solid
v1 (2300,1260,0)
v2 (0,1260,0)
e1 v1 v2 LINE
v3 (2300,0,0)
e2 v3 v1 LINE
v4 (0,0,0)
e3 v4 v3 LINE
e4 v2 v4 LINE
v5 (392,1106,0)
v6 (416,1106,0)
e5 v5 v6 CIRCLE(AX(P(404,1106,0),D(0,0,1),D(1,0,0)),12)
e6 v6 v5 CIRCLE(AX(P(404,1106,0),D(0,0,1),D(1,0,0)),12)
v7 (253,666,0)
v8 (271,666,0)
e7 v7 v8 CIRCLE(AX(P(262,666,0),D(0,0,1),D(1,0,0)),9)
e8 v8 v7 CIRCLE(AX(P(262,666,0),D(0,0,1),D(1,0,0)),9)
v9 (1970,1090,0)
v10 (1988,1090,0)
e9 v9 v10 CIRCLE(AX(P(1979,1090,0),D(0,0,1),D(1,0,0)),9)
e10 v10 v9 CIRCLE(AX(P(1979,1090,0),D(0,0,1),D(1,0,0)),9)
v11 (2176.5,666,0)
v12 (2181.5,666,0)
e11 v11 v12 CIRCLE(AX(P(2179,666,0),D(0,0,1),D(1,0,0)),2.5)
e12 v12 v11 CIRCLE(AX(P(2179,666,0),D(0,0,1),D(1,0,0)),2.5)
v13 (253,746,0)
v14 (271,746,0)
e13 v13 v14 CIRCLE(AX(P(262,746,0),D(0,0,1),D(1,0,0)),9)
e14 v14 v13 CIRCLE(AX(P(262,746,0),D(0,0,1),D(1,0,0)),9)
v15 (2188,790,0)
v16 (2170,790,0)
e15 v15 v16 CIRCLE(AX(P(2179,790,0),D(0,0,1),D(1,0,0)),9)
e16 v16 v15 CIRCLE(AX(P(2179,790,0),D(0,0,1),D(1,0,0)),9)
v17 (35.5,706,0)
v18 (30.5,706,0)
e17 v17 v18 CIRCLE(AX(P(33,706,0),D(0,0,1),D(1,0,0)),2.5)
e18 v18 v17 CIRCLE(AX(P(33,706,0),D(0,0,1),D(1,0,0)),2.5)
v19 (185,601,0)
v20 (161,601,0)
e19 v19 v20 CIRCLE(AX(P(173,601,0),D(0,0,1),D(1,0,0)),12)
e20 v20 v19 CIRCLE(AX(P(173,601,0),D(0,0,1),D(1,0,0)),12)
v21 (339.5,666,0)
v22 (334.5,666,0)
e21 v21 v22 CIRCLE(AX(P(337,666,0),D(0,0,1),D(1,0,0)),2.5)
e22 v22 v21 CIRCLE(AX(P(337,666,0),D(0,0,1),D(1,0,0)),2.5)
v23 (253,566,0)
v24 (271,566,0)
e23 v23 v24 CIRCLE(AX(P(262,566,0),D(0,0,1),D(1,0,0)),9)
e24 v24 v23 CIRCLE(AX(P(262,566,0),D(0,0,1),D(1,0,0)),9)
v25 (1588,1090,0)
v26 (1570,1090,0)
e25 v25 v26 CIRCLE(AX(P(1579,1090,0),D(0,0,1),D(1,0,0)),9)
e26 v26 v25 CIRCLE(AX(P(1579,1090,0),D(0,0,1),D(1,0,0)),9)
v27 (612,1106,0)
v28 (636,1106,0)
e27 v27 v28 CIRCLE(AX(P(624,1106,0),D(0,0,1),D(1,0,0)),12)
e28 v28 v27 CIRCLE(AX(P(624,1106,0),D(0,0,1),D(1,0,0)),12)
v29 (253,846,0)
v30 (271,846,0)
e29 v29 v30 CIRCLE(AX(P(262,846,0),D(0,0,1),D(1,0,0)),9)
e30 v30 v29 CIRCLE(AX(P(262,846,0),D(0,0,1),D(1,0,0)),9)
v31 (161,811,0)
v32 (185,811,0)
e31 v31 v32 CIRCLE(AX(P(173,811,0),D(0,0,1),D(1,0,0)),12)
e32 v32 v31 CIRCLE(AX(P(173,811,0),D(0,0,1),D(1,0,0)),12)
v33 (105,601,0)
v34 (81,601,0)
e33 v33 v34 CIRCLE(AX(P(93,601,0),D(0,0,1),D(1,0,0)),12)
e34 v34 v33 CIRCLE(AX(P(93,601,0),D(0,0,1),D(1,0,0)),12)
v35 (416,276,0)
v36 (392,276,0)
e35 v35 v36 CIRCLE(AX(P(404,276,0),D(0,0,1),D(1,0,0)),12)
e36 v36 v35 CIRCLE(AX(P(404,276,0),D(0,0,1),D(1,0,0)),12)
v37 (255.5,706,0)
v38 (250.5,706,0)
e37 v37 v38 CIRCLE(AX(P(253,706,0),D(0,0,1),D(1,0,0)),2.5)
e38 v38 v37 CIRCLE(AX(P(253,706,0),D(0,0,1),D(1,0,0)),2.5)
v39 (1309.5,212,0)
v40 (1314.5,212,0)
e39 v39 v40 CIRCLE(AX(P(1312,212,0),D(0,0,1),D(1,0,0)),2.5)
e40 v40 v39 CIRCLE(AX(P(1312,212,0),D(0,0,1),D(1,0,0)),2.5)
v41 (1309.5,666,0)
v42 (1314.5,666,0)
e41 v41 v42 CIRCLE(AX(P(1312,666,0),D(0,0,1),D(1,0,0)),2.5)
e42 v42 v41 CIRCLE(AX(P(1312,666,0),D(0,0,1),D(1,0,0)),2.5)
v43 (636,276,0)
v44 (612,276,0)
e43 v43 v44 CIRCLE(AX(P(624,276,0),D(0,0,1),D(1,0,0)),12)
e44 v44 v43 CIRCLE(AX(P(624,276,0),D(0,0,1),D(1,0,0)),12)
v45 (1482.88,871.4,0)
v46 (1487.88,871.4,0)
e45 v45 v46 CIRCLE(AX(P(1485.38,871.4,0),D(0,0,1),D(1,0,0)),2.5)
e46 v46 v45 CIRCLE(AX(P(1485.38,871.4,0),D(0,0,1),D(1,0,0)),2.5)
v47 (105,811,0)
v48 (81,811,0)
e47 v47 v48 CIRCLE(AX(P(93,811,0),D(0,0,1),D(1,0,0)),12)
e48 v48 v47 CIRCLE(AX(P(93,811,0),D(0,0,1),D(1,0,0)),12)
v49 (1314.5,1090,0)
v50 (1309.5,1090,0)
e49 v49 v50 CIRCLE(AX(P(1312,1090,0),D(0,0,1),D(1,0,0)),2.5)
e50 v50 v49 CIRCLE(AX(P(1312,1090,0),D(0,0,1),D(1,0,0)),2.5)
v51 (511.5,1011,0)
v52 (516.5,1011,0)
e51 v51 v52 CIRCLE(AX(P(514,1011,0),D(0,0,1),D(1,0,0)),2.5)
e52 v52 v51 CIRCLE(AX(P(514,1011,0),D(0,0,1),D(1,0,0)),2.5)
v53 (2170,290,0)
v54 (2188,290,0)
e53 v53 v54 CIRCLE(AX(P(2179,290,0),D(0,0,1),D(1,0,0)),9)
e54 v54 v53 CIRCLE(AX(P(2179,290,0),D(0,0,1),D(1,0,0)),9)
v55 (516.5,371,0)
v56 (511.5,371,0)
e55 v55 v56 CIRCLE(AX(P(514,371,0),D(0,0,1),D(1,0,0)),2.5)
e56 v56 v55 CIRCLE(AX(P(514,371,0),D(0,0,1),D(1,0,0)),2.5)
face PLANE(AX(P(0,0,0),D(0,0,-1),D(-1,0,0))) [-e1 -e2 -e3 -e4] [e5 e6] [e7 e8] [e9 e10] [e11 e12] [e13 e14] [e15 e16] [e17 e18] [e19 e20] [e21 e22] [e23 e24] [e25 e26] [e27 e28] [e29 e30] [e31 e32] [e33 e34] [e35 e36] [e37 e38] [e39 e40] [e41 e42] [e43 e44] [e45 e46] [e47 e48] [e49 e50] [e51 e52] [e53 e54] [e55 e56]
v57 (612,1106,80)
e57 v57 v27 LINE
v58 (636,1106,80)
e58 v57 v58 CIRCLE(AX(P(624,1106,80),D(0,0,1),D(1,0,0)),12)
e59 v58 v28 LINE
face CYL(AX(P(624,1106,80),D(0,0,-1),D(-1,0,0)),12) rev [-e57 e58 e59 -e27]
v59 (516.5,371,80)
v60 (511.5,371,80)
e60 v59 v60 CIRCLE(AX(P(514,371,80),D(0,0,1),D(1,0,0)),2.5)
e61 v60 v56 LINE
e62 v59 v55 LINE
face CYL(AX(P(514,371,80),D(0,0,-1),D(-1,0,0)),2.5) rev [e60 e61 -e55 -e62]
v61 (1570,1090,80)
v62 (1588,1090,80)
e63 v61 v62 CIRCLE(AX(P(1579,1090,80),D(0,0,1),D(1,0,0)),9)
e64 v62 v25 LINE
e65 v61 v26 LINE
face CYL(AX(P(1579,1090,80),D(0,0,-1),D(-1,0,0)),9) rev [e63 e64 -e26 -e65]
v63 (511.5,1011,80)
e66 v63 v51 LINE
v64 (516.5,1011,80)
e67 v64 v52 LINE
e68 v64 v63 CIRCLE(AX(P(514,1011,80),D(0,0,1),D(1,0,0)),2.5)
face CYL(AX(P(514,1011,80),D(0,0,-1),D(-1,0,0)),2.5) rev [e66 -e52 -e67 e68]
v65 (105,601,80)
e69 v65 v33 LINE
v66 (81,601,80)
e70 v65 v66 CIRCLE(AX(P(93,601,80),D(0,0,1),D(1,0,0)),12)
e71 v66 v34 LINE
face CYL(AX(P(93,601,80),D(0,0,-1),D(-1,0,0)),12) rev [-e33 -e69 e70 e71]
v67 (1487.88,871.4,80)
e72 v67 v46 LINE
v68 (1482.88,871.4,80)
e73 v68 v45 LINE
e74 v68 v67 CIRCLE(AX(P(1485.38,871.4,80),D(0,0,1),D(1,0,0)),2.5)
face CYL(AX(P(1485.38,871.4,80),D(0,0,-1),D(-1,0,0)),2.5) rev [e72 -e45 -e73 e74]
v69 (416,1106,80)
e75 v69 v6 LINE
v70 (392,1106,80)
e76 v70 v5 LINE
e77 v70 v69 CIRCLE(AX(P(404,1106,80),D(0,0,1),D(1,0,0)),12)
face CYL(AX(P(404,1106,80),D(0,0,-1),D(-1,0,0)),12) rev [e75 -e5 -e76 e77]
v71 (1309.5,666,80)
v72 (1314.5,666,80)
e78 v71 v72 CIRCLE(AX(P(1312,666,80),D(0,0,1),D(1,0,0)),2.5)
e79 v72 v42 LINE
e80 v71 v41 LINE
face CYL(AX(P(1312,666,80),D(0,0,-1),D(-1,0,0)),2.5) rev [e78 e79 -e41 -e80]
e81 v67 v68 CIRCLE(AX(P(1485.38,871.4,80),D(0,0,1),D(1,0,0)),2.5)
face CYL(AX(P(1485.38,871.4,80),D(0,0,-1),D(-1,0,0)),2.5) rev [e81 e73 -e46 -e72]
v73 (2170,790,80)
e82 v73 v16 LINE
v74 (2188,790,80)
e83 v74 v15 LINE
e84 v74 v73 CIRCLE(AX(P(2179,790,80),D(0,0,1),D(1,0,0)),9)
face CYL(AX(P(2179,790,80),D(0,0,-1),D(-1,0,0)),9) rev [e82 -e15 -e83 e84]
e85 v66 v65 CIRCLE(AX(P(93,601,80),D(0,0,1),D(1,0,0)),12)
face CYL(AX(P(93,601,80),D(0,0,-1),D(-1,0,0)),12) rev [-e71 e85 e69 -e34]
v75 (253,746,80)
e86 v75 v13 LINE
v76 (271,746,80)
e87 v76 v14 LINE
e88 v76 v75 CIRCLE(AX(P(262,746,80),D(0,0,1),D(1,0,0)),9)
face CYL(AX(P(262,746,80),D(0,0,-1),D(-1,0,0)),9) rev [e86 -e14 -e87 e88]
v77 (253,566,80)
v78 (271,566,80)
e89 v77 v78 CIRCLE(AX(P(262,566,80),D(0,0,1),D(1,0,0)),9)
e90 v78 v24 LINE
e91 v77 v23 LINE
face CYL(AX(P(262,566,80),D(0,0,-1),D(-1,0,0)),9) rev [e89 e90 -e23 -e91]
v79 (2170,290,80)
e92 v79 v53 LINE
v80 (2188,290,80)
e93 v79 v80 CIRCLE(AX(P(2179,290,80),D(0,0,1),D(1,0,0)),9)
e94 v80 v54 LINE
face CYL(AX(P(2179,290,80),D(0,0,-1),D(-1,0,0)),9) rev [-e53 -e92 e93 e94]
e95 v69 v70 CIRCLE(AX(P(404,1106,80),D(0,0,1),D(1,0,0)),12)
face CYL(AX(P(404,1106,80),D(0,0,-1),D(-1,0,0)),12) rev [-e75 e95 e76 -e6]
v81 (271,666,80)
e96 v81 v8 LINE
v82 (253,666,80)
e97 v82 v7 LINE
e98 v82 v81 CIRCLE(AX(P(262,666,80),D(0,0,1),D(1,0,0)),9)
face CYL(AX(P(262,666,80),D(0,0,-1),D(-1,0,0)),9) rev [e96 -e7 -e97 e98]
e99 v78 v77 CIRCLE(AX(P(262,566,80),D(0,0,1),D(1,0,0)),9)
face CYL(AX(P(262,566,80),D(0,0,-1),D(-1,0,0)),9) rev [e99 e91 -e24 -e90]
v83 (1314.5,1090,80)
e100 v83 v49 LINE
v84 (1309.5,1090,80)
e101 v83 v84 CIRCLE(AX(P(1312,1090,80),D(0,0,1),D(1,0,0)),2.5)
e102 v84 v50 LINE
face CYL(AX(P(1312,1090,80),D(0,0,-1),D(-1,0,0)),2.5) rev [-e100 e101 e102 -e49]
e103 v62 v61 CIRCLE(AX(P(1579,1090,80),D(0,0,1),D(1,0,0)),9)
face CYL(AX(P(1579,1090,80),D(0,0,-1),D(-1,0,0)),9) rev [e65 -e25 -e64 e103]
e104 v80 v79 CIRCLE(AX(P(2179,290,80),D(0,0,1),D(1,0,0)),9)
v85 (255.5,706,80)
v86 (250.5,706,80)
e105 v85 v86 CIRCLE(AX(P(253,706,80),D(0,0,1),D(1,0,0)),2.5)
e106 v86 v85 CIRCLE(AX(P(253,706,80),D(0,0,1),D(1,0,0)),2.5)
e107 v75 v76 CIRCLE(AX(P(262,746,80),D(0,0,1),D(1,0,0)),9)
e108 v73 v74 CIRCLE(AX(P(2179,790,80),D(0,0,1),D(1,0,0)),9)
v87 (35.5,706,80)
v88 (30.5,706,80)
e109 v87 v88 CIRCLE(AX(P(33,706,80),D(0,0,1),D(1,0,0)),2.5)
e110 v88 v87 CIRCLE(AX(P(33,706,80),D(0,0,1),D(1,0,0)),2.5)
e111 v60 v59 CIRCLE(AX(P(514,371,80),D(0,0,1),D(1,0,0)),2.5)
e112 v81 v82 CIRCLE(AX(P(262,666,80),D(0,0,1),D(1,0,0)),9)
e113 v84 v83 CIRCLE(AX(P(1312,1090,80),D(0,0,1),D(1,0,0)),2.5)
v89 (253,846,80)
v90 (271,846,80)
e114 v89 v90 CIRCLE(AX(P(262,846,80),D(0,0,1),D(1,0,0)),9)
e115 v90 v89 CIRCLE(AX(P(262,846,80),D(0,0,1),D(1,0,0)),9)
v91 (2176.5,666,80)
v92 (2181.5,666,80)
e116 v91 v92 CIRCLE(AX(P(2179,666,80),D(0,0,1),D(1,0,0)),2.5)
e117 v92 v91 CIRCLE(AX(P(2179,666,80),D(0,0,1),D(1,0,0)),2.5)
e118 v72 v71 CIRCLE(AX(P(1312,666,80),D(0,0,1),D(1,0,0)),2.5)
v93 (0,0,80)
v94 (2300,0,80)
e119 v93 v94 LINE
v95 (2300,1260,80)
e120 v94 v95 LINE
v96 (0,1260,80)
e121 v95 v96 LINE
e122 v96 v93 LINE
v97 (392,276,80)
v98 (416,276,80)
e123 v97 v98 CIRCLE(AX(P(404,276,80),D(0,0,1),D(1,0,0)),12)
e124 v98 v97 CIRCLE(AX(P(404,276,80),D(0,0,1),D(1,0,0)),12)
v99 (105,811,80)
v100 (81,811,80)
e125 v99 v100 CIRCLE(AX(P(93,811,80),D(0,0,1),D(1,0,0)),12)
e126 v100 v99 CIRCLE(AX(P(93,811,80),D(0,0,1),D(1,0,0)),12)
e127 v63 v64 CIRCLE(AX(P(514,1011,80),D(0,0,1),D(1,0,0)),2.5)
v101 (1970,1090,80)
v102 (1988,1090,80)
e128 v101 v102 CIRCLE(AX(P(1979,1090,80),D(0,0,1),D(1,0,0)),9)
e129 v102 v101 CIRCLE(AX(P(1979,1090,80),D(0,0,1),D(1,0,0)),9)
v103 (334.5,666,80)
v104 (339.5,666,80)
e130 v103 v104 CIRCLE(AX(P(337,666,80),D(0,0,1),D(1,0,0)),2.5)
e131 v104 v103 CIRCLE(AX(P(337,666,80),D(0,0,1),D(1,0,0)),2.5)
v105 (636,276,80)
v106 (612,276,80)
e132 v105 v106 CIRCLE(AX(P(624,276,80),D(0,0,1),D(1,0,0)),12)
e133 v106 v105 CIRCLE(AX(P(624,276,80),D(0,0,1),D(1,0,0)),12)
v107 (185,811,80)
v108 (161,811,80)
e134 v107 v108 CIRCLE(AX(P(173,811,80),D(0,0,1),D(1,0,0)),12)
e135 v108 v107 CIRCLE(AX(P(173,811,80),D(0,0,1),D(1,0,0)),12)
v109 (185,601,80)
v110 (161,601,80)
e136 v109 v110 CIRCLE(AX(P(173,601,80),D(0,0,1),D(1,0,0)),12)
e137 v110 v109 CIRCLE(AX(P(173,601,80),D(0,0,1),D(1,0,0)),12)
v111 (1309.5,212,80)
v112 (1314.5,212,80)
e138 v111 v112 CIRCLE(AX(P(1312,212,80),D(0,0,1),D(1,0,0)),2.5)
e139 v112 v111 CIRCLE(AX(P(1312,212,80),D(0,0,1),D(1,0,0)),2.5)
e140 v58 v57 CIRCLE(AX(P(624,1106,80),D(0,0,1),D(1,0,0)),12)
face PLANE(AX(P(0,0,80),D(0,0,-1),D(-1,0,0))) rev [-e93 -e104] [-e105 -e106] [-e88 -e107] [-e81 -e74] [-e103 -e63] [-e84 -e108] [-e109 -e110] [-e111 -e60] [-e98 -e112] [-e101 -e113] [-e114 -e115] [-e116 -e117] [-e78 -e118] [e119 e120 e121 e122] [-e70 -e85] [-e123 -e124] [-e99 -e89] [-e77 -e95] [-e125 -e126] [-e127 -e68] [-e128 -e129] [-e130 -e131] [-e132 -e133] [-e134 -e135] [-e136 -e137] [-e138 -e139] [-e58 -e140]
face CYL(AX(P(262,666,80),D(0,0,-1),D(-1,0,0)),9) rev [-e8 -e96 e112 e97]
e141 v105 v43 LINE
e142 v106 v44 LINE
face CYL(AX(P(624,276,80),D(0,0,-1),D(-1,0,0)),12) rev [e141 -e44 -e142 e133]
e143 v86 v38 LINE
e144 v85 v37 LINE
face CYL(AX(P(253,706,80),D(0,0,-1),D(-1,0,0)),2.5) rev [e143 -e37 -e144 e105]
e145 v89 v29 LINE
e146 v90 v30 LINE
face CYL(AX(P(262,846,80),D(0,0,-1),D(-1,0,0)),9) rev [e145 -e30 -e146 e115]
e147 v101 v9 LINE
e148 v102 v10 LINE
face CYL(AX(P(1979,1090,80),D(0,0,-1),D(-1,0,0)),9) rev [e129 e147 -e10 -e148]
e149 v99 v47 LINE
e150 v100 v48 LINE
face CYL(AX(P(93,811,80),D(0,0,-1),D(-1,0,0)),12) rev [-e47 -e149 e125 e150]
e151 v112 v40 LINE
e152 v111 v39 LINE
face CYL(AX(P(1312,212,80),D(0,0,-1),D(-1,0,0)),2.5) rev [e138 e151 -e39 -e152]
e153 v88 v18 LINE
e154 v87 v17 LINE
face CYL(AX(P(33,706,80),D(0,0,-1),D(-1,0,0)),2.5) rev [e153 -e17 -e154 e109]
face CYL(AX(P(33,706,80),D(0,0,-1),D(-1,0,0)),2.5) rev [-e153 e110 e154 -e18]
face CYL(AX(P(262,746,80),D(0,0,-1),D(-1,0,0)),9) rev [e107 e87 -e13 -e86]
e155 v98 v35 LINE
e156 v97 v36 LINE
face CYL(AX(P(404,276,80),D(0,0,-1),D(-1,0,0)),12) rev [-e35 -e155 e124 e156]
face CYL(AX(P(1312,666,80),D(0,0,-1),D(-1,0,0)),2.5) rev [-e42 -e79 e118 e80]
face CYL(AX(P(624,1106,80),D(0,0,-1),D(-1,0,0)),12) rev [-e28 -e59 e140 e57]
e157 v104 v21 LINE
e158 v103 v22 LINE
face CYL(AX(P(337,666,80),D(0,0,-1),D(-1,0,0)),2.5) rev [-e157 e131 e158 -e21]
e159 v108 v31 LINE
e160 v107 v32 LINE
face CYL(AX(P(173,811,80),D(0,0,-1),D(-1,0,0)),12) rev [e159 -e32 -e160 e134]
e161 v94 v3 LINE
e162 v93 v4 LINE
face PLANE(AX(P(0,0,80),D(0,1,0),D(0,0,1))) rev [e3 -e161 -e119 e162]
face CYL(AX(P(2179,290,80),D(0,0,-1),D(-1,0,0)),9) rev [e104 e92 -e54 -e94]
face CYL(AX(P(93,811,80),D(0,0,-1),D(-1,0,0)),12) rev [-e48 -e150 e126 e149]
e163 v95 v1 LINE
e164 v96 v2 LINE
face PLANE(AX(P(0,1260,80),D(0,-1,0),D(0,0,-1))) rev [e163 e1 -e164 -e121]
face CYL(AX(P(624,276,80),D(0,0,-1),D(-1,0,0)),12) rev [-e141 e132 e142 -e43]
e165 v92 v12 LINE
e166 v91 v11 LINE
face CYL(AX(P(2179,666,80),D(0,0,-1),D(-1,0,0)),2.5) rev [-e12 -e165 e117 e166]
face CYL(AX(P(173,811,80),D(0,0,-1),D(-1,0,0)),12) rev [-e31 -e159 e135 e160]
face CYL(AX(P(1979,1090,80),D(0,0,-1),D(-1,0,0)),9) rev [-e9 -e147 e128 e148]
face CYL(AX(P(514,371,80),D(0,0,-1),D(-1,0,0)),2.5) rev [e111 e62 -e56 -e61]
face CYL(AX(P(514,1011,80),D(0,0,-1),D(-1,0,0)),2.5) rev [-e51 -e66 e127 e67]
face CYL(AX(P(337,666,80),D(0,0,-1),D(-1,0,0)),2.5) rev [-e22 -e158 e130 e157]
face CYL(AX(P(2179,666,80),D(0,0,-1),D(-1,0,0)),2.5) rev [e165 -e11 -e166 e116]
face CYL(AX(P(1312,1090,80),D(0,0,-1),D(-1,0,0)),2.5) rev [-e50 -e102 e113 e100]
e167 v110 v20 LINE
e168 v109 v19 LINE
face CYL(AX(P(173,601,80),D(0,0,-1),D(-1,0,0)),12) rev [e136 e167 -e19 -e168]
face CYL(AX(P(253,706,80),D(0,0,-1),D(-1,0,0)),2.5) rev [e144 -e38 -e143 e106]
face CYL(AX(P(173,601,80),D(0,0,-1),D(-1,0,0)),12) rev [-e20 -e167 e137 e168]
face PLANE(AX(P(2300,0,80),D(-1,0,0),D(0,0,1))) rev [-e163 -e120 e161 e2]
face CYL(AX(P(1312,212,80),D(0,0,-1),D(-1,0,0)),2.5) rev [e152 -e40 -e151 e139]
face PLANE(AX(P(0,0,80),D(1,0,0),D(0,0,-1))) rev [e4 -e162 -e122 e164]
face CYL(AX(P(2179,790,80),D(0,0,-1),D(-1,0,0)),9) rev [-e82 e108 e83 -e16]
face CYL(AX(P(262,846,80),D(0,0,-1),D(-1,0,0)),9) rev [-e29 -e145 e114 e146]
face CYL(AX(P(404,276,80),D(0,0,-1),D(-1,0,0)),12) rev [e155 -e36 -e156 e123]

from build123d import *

# Parameters (mm, degrees)
SKETCH1_W           = 2300
SKETCH1_H           = 1260
SKETCH1_R           = 9
SKETCH1_R_2         = 12
SKETCH1_R_3         = 2.5
BOSS_EXTRUDE1_DEPTH = 80


with BuildPart() as part:
    # Sketch1 → Boss-Extrude1 (new body)
    with BuildSketch(Plane.XY):
        with Locations((1150, 630)):
            Rectangle(SKETCH1_W, SKETCH1_H)
        with Locations((1579, 1090)):
            Circle(SKETCH1_R, mode=Mode.SUBTRACT)
        with Locations((1979, 1090)):
            Circle(SKETCH1_R, mode=Mode.SUBTRACT)
        with Locations((2179, 790)):
            Circle(SKETCH1_R, mode=Mode.SUBTRACT)
        with Locations((2179, 290)):
            Circle(SKETCH1_R, mode=Mode.SUBTRACT)
        with Locations((93, 811)):
            Circle(SKETCH1_R_2, mode=Mode.SUBTRACT)
        with Locations((173, 811)):
            Circle(SKETCH1_R_2, mode=Mode.SUBTRACT)
        with Locations((93, 601)):
            Circle(SKETCH1_R_2, mode=Mode.SUBTRACT)
        with Locations((173, 601)):
            Circle(SKETCH1_R_2, mode=Mode.SUBTRACT)
        with Locations((404, 1106)):
            Circle(SKETCH1_R_2, mode=Mode.SUBTRACT)
        with Locations((624, 1106)):
            Circle(SKETCH1_R_2, mode=Mode.SUBTRACT)
        with Locations((404, 276)):
            Circle(SKETCH1_R_2, mode=Mode.SUBTRACT)
        with Locations((624, 276)):
            Circle(SKETCH1_R_2, mode=Mode.SUBTRACT)
        with Locations((2179, 666)):
            Circle(SKETCH1_R_3, mode=Mode.SUBTRACT)
        with Locations((337, 666)):
            Circle(SKETCH1_R_3, mode=Mode.SUBTRACT)
        with Locations((1312, 666)):
            Circle(SKETCH1_R_3, mode=Mode.SUBTRACT)
        with Locations((1485.38, 871.4)):
            Circle(SKETCH1_R_3, mode=Mode.SUBTRACT)
        with Locations((1312, 1090)):
            Circle(SKETCH1_R_3, mode=Mode.SUBTRACT)
        with Locations((1312, 212)):
            Circle(SKETCH1_R_3, mode=Mode.SUBTRACT)
        with Locations((514, 371)):
            Circle(SKETCH1_R_3, mode=Mode.SUBTRACT)
        with Locations((514, 1011)):
            Circle(SKETCH1_R_3, mode=Mode.SUBTRACT)
        with Locations((253, 706)):
            Circle(SKETCH1_R_3, mode=Mode.SUBTRACT)
        with Locations((33, 706)):
            Circle(SKETCH1_R_3, mode=Mode.SUBTRACT)
        with Locations((262, 746)):
            Circle(SKETCH1_R, mode=Mode.SUBTRACT)
        with Locations((262, 846)):
            Circle(SKETCH1_R, mode=Mode.SUBTRACT)
        with Locations((262, 666)):
            Circle(SKETCH1_R, mode=Mode.SUBTRACT)
        with Locations((262, 566)):
            Circle(SKETCH1_R, mode=Mode.SUBTRACT)
    extrude(amount=BOSS_EXTRUDE1_DEPTH)


solid = part.part
